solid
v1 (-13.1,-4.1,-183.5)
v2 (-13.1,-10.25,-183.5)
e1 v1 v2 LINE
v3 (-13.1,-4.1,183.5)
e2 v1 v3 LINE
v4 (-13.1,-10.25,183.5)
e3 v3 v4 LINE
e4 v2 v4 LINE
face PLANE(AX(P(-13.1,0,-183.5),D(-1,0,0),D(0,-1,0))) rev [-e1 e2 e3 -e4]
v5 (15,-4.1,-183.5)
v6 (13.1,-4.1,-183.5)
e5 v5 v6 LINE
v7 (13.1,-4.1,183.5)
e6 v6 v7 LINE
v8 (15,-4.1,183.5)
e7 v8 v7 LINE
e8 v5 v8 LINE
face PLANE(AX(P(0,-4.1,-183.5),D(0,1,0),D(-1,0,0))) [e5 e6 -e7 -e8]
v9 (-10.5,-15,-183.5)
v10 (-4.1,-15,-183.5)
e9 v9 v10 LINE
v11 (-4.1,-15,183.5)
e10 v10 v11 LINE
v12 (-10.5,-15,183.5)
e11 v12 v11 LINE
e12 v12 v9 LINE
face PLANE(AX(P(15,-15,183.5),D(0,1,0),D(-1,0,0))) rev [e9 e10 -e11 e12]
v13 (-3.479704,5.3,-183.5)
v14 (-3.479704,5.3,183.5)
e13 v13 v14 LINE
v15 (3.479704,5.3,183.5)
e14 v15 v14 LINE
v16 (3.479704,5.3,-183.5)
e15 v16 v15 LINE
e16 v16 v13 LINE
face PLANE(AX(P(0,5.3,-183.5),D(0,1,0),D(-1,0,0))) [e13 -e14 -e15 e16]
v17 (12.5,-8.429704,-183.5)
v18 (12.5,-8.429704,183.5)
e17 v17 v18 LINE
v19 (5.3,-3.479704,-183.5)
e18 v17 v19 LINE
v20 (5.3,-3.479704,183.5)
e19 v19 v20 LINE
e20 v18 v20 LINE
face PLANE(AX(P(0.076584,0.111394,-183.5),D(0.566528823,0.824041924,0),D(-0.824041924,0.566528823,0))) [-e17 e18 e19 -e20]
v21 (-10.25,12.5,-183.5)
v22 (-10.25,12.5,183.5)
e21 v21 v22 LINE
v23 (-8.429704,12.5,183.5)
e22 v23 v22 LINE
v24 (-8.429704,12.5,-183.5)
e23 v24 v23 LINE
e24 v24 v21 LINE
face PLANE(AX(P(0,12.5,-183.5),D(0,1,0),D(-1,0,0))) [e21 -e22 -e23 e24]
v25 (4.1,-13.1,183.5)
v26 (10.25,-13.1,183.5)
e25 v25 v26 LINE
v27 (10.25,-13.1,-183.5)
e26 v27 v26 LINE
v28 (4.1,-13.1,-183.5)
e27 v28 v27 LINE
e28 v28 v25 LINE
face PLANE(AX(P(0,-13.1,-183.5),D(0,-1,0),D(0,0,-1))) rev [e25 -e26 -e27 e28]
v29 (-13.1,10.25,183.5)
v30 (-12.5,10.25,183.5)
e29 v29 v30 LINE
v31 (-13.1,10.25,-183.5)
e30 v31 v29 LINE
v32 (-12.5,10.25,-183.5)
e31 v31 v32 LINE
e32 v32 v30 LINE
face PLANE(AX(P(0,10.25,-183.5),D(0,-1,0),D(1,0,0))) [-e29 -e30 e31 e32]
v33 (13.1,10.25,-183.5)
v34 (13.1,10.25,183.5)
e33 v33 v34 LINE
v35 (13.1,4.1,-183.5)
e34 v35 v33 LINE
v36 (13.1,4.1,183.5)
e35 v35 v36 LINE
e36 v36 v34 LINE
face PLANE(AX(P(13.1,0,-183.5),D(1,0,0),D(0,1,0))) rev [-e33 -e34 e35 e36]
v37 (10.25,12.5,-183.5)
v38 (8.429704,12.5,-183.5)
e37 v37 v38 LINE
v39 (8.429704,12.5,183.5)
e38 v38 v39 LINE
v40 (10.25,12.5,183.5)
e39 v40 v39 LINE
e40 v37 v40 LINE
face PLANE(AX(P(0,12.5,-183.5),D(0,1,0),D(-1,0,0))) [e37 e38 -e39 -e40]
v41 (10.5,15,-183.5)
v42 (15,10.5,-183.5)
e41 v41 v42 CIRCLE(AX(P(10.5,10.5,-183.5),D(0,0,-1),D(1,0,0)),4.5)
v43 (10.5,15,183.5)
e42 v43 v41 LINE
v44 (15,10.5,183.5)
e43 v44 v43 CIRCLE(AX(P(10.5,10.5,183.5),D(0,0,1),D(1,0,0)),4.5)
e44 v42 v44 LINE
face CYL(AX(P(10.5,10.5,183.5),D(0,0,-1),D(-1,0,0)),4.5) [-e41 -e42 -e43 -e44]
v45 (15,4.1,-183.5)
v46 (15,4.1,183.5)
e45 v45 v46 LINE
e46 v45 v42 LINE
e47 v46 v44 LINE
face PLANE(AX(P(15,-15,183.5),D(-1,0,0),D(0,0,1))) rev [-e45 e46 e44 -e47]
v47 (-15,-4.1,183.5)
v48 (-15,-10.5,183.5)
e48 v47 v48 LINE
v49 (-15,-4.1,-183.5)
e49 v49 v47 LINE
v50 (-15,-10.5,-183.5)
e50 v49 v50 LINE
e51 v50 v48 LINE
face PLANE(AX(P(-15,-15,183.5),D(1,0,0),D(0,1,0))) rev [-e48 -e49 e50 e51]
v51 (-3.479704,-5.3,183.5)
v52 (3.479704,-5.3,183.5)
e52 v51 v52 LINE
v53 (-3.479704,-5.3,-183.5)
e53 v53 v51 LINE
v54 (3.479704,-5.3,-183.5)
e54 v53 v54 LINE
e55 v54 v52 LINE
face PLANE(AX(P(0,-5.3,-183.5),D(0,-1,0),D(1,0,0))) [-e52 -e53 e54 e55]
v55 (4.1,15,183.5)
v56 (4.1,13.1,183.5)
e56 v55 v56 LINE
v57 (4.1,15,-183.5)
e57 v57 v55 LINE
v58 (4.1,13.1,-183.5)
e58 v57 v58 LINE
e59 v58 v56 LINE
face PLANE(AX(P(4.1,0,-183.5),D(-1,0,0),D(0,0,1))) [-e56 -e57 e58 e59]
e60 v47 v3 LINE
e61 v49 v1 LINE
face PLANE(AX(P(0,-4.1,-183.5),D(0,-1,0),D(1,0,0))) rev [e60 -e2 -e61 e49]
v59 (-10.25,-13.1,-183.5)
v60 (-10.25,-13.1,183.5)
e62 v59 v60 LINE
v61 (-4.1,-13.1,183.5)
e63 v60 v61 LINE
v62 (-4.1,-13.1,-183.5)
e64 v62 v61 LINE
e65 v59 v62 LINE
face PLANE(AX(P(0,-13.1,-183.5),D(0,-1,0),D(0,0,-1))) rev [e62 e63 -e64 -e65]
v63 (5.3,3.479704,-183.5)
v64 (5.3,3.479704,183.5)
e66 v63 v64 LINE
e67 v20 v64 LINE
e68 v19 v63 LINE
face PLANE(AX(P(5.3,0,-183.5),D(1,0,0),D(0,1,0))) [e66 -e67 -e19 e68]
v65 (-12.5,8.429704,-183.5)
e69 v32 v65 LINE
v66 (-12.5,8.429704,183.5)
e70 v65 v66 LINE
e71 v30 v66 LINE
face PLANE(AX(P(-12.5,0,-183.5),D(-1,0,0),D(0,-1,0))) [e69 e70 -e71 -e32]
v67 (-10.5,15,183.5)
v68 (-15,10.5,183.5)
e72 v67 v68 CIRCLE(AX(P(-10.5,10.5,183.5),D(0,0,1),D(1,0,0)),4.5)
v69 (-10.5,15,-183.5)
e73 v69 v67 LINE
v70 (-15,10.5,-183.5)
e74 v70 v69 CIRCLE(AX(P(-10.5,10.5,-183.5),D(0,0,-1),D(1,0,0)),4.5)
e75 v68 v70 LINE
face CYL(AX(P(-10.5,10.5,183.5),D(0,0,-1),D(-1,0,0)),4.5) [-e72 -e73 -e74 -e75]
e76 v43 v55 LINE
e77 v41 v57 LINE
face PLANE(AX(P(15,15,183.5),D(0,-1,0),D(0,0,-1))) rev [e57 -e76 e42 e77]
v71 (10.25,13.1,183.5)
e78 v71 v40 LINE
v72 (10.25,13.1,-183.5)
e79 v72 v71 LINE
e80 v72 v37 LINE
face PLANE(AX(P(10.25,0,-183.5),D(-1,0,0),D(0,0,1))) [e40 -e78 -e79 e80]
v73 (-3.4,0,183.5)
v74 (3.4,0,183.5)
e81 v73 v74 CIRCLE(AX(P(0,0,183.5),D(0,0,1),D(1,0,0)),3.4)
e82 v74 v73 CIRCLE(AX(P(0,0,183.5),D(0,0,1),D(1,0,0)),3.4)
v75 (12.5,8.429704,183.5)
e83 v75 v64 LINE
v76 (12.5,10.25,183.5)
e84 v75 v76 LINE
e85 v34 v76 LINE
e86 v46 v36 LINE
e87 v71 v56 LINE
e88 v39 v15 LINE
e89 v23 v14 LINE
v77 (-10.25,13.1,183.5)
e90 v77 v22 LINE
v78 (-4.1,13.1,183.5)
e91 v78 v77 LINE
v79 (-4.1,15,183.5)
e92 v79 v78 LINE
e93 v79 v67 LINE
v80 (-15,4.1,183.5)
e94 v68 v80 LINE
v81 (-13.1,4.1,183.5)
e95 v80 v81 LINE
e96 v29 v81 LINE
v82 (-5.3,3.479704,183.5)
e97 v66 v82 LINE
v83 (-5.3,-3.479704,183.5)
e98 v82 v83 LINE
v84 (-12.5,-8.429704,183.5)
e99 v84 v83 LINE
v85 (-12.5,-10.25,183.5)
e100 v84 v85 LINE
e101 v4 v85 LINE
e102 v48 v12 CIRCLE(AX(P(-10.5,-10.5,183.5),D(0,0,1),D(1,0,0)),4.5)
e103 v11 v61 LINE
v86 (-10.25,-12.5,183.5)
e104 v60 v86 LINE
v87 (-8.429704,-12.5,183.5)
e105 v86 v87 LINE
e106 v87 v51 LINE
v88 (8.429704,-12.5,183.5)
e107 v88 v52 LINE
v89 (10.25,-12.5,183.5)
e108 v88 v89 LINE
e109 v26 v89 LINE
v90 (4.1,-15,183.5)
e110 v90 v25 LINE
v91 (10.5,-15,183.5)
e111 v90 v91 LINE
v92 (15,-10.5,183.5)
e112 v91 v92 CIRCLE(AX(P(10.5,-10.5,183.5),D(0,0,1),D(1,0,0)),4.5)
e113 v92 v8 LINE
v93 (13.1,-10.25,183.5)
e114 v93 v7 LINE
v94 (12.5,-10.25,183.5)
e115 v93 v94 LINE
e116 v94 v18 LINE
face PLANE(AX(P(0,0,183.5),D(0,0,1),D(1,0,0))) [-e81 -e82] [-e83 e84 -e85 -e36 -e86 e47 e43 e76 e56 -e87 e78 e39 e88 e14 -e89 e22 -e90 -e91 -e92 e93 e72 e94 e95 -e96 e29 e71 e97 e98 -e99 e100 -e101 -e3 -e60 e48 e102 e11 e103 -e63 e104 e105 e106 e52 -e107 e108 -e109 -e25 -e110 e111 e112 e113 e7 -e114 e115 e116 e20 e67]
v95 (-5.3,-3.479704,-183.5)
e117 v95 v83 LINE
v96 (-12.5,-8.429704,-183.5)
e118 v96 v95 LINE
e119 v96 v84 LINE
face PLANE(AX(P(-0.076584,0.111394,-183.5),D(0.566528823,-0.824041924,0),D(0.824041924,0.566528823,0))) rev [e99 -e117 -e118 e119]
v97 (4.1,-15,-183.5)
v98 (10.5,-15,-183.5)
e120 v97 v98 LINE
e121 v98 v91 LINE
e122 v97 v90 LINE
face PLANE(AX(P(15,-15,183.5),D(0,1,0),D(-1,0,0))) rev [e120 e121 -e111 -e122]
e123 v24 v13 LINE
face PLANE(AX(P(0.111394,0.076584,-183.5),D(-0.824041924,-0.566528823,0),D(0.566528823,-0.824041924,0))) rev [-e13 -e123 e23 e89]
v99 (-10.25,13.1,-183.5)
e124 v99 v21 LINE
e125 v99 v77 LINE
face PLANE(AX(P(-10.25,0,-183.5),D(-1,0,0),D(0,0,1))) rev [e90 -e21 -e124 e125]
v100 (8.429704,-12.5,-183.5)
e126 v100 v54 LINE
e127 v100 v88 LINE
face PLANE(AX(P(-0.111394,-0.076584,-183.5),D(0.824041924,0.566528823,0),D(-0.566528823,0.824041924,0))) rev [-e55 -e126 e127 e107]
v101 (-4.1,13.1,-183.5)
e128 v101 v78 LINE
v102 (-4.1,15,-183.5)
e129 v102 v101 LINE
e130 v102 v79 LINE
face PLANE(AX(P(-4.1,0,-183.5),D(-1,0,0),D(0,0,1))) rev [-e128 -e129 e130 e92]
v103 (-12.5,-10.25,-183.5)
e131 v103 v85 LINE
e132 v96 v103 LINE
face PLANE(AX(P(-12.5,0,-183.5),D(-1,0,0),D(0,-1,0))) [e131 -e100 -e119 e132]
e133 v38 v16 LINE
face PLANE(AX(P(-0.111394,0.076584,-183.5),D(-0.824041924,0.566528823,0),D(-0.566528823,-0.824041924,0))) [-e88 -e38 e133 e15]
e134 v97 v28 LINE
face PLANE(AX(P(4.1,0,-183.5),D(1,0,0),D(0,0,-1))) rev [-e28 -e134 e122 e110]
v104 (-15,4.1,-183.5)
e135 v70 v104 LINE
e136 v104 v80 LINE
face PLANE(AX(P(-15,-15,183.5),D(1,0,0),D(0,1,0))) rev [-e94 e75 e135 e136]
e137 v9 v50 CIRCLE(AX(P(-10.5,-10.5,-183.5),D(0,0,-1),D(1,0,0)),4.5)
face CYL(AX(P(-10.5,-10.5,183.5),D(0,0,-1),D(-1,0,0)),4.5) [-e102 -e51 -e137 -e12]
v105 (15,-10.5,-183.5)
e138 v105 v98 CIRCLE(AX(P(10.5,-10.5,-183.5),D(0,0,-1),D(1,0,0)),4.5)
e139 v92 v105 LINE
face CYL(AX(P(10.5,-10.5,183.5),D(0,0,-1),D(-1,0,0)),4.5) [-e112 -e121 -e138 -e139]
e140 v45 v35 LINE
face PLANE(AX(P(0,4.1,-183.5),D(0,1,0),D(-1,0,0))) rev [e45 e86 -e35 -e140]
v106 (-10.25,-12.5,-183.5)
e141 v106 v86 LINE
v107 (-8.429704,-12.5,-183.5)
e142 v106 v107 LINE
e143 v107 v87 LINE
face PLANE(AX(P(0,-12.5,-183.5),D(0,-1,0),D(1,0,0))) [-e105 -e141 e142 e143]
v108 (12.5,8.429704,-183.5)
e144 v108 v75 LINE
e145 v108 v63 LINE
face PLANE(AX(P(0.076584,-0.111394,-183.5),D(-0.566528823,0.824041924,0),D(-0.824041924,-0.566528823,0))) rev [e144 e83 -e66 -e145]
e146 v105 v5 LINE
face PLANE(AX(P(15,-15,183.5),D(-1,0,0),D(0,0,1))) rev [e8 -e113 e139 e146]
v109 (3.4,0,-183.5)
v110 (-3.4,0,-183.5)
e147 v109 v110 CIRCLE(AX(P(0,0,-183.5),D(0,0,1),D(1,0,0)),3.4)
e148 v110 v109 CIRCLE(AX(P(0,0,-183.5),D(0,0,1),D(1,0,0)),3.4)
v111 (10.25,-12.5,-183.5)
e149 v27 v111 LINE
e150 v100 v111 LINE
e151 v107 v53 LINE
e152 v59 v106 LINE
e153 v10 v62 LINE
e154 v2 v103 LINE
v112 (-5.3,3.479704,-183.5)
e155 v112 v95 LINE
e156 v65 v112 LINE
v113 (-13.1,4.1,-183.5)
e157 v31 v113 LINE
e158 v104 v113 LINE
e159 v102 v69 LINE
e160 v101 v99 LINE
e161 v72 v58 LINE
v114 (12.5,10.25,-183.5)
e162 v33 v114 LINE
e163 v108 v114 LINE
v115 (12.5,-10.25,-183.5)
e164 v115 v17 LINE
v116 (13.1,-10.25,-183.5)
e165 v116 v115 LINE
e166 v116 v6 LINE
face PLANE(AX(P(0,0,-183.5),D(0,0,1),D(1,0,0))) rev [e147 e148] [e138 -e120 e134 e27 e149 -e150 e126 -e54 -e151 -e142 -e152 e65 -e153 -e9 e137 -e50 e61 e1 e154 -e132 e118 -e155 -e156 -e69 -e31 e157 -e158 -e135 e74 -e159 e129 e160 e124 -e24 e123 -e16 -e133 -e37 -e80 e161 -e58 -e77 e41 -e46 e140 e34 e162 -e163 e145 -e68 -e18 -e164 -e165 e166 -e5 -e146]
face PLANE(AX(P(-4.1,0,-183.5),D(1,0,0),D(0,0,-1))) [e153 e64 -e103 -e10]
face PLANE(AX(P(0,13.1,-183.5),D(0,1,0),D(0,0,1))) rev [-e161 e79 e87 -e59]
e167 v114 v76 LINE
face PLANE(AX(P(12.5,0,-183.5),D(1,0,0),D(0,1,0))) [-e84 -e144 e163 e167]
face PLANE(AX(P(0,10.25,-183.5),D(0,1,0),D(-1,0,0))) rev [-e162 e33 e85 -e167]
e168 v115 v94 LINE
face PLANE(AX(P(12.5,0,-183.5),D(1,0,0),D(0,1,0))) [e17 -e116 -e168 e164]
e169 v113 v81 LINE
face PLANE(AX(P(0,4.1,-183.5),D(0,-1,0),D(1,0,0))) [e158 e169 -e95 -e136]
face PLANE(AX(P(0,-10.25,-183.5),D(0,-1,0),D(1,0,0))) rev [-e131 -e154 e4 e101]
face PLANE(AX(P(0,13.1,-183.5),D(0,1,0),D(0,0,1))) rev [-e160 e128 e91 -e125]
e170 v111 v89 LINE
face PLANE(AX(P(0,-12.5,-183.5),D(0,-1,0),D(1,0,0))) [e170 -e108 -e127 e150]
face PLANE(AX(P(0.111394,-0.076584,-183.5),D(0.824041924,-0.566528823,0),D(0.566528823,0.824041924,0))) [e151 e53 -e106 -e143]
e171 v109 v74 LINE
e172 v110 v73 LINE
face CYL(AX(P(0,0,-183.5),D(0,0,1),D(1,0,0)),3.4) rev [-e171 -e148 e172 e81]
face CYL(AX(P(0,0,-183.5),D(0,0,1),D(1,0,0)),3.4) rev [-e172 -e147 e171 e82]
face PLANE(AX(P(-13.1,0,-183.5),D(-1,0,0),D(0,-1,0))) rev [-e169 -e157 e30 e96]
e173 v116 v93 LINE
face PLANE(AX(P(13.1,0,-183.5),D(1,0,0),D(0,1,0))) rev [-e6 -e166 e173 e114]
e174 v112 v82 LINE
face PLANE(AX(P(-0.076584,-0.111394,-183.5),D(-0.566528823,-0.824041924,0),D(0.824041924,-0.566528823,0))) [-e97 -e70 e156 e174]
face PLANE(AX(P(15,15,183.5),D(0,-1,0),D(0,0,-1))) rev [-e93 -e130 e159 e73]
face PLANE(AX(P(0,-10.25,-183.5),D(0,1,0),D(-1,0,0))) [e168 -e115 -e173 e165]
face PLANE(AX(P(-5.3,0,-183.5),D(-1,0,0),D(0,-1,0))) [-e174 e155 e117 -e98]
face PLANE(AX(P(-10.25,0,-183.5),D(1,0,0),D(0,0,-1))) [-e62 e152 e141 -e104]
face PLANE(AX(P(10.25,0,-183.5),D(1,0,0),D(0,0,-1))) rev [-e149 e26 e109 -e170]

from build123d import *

# Parameters (mm, degrees)
SKETCH_1_W               = 30
SKETCH_1_H               = 30
EXTRUDE_1_DEPTH          = 183.5
FILLET_1_R               = 4.5
SKETCH_2_W               = 8.2
SKETCH_2_H               = 0.3
SKETCH_2_H_2             = 1.9
SKETCH_2_R               = 3.4
CUT_EXTRUDE_1_DEPTH      = 368.612567794
PATTERN_CIRCULAR_1_COUNT = 4


with BuildPart() as part:
    # 草图1 → 凸台-拉伸1 (new, symmetric)
    with BuildSketch(Plane.XY):
        Rectangle(SKETCH_1_W, SKETCH_1_H)
    extrude(amount=EXTRUDE_1_DEPTH, both=True)

    # 圆角1
    fillet_1_edges = [part.edges().sort_by_distance(p)[0] for p in [
        (-15, 15, 0),
        (15, 15, 0),
        (15, -15, 0),
        (-15, -15, 0),
    ]]
    fillet(fillet_1_edges, radius=FILLET_1_R)

    # 草图2 → 切除-拉伸1 (cut, through all)
    with BuildSketch(Plane.XY.offset(183.5)):
        with Locations((0, 12.95)):
            Rectangle(SKETCH_2_W, SKETCH_2_H)
        with Locations((0, 14.05)):
            Rectangle(SKETCH_2_W, SKETCH_2_H_2)
        Polygon((10.25, 13.1), (4.1, 13.1), (4.1, 12.8), (-4.1, 12.8), (-4.1, 13.1), (-10.25, 13.1), (-10.25, 12.5), (-8.429704265, 12.5), (8.429704265, 12.5), (10.25, 12.5), align=None)
        Polygon((3.479704265, 5.3), (8.429704265, 12.5), (-8.429704265, 12.5), (-3.479704265, 5.3), align=None)
        Circle(SKETCH_2_R)
    cut_extrude_1 = extrude(amount=-CUT_EXTRUDE_1_DEPTH, mode=Mode.SUBTRACT)

    # 阵列(圆周)1: 切除-拉伸1 ×4 about axis
    pattern_circular_1_axis = Axis((0, 0, 0), (0, 0, 1))
    for i in range(1, PATTERN_CIRCULAR_1_COUNT):
        add(cut_extrude_1.rotate(pattern_circular_1_axis, i * 360 / PATTERN_CIRCULAR_1_COUNT), mode=Mode.SUBTRACT)


solid = part.part
